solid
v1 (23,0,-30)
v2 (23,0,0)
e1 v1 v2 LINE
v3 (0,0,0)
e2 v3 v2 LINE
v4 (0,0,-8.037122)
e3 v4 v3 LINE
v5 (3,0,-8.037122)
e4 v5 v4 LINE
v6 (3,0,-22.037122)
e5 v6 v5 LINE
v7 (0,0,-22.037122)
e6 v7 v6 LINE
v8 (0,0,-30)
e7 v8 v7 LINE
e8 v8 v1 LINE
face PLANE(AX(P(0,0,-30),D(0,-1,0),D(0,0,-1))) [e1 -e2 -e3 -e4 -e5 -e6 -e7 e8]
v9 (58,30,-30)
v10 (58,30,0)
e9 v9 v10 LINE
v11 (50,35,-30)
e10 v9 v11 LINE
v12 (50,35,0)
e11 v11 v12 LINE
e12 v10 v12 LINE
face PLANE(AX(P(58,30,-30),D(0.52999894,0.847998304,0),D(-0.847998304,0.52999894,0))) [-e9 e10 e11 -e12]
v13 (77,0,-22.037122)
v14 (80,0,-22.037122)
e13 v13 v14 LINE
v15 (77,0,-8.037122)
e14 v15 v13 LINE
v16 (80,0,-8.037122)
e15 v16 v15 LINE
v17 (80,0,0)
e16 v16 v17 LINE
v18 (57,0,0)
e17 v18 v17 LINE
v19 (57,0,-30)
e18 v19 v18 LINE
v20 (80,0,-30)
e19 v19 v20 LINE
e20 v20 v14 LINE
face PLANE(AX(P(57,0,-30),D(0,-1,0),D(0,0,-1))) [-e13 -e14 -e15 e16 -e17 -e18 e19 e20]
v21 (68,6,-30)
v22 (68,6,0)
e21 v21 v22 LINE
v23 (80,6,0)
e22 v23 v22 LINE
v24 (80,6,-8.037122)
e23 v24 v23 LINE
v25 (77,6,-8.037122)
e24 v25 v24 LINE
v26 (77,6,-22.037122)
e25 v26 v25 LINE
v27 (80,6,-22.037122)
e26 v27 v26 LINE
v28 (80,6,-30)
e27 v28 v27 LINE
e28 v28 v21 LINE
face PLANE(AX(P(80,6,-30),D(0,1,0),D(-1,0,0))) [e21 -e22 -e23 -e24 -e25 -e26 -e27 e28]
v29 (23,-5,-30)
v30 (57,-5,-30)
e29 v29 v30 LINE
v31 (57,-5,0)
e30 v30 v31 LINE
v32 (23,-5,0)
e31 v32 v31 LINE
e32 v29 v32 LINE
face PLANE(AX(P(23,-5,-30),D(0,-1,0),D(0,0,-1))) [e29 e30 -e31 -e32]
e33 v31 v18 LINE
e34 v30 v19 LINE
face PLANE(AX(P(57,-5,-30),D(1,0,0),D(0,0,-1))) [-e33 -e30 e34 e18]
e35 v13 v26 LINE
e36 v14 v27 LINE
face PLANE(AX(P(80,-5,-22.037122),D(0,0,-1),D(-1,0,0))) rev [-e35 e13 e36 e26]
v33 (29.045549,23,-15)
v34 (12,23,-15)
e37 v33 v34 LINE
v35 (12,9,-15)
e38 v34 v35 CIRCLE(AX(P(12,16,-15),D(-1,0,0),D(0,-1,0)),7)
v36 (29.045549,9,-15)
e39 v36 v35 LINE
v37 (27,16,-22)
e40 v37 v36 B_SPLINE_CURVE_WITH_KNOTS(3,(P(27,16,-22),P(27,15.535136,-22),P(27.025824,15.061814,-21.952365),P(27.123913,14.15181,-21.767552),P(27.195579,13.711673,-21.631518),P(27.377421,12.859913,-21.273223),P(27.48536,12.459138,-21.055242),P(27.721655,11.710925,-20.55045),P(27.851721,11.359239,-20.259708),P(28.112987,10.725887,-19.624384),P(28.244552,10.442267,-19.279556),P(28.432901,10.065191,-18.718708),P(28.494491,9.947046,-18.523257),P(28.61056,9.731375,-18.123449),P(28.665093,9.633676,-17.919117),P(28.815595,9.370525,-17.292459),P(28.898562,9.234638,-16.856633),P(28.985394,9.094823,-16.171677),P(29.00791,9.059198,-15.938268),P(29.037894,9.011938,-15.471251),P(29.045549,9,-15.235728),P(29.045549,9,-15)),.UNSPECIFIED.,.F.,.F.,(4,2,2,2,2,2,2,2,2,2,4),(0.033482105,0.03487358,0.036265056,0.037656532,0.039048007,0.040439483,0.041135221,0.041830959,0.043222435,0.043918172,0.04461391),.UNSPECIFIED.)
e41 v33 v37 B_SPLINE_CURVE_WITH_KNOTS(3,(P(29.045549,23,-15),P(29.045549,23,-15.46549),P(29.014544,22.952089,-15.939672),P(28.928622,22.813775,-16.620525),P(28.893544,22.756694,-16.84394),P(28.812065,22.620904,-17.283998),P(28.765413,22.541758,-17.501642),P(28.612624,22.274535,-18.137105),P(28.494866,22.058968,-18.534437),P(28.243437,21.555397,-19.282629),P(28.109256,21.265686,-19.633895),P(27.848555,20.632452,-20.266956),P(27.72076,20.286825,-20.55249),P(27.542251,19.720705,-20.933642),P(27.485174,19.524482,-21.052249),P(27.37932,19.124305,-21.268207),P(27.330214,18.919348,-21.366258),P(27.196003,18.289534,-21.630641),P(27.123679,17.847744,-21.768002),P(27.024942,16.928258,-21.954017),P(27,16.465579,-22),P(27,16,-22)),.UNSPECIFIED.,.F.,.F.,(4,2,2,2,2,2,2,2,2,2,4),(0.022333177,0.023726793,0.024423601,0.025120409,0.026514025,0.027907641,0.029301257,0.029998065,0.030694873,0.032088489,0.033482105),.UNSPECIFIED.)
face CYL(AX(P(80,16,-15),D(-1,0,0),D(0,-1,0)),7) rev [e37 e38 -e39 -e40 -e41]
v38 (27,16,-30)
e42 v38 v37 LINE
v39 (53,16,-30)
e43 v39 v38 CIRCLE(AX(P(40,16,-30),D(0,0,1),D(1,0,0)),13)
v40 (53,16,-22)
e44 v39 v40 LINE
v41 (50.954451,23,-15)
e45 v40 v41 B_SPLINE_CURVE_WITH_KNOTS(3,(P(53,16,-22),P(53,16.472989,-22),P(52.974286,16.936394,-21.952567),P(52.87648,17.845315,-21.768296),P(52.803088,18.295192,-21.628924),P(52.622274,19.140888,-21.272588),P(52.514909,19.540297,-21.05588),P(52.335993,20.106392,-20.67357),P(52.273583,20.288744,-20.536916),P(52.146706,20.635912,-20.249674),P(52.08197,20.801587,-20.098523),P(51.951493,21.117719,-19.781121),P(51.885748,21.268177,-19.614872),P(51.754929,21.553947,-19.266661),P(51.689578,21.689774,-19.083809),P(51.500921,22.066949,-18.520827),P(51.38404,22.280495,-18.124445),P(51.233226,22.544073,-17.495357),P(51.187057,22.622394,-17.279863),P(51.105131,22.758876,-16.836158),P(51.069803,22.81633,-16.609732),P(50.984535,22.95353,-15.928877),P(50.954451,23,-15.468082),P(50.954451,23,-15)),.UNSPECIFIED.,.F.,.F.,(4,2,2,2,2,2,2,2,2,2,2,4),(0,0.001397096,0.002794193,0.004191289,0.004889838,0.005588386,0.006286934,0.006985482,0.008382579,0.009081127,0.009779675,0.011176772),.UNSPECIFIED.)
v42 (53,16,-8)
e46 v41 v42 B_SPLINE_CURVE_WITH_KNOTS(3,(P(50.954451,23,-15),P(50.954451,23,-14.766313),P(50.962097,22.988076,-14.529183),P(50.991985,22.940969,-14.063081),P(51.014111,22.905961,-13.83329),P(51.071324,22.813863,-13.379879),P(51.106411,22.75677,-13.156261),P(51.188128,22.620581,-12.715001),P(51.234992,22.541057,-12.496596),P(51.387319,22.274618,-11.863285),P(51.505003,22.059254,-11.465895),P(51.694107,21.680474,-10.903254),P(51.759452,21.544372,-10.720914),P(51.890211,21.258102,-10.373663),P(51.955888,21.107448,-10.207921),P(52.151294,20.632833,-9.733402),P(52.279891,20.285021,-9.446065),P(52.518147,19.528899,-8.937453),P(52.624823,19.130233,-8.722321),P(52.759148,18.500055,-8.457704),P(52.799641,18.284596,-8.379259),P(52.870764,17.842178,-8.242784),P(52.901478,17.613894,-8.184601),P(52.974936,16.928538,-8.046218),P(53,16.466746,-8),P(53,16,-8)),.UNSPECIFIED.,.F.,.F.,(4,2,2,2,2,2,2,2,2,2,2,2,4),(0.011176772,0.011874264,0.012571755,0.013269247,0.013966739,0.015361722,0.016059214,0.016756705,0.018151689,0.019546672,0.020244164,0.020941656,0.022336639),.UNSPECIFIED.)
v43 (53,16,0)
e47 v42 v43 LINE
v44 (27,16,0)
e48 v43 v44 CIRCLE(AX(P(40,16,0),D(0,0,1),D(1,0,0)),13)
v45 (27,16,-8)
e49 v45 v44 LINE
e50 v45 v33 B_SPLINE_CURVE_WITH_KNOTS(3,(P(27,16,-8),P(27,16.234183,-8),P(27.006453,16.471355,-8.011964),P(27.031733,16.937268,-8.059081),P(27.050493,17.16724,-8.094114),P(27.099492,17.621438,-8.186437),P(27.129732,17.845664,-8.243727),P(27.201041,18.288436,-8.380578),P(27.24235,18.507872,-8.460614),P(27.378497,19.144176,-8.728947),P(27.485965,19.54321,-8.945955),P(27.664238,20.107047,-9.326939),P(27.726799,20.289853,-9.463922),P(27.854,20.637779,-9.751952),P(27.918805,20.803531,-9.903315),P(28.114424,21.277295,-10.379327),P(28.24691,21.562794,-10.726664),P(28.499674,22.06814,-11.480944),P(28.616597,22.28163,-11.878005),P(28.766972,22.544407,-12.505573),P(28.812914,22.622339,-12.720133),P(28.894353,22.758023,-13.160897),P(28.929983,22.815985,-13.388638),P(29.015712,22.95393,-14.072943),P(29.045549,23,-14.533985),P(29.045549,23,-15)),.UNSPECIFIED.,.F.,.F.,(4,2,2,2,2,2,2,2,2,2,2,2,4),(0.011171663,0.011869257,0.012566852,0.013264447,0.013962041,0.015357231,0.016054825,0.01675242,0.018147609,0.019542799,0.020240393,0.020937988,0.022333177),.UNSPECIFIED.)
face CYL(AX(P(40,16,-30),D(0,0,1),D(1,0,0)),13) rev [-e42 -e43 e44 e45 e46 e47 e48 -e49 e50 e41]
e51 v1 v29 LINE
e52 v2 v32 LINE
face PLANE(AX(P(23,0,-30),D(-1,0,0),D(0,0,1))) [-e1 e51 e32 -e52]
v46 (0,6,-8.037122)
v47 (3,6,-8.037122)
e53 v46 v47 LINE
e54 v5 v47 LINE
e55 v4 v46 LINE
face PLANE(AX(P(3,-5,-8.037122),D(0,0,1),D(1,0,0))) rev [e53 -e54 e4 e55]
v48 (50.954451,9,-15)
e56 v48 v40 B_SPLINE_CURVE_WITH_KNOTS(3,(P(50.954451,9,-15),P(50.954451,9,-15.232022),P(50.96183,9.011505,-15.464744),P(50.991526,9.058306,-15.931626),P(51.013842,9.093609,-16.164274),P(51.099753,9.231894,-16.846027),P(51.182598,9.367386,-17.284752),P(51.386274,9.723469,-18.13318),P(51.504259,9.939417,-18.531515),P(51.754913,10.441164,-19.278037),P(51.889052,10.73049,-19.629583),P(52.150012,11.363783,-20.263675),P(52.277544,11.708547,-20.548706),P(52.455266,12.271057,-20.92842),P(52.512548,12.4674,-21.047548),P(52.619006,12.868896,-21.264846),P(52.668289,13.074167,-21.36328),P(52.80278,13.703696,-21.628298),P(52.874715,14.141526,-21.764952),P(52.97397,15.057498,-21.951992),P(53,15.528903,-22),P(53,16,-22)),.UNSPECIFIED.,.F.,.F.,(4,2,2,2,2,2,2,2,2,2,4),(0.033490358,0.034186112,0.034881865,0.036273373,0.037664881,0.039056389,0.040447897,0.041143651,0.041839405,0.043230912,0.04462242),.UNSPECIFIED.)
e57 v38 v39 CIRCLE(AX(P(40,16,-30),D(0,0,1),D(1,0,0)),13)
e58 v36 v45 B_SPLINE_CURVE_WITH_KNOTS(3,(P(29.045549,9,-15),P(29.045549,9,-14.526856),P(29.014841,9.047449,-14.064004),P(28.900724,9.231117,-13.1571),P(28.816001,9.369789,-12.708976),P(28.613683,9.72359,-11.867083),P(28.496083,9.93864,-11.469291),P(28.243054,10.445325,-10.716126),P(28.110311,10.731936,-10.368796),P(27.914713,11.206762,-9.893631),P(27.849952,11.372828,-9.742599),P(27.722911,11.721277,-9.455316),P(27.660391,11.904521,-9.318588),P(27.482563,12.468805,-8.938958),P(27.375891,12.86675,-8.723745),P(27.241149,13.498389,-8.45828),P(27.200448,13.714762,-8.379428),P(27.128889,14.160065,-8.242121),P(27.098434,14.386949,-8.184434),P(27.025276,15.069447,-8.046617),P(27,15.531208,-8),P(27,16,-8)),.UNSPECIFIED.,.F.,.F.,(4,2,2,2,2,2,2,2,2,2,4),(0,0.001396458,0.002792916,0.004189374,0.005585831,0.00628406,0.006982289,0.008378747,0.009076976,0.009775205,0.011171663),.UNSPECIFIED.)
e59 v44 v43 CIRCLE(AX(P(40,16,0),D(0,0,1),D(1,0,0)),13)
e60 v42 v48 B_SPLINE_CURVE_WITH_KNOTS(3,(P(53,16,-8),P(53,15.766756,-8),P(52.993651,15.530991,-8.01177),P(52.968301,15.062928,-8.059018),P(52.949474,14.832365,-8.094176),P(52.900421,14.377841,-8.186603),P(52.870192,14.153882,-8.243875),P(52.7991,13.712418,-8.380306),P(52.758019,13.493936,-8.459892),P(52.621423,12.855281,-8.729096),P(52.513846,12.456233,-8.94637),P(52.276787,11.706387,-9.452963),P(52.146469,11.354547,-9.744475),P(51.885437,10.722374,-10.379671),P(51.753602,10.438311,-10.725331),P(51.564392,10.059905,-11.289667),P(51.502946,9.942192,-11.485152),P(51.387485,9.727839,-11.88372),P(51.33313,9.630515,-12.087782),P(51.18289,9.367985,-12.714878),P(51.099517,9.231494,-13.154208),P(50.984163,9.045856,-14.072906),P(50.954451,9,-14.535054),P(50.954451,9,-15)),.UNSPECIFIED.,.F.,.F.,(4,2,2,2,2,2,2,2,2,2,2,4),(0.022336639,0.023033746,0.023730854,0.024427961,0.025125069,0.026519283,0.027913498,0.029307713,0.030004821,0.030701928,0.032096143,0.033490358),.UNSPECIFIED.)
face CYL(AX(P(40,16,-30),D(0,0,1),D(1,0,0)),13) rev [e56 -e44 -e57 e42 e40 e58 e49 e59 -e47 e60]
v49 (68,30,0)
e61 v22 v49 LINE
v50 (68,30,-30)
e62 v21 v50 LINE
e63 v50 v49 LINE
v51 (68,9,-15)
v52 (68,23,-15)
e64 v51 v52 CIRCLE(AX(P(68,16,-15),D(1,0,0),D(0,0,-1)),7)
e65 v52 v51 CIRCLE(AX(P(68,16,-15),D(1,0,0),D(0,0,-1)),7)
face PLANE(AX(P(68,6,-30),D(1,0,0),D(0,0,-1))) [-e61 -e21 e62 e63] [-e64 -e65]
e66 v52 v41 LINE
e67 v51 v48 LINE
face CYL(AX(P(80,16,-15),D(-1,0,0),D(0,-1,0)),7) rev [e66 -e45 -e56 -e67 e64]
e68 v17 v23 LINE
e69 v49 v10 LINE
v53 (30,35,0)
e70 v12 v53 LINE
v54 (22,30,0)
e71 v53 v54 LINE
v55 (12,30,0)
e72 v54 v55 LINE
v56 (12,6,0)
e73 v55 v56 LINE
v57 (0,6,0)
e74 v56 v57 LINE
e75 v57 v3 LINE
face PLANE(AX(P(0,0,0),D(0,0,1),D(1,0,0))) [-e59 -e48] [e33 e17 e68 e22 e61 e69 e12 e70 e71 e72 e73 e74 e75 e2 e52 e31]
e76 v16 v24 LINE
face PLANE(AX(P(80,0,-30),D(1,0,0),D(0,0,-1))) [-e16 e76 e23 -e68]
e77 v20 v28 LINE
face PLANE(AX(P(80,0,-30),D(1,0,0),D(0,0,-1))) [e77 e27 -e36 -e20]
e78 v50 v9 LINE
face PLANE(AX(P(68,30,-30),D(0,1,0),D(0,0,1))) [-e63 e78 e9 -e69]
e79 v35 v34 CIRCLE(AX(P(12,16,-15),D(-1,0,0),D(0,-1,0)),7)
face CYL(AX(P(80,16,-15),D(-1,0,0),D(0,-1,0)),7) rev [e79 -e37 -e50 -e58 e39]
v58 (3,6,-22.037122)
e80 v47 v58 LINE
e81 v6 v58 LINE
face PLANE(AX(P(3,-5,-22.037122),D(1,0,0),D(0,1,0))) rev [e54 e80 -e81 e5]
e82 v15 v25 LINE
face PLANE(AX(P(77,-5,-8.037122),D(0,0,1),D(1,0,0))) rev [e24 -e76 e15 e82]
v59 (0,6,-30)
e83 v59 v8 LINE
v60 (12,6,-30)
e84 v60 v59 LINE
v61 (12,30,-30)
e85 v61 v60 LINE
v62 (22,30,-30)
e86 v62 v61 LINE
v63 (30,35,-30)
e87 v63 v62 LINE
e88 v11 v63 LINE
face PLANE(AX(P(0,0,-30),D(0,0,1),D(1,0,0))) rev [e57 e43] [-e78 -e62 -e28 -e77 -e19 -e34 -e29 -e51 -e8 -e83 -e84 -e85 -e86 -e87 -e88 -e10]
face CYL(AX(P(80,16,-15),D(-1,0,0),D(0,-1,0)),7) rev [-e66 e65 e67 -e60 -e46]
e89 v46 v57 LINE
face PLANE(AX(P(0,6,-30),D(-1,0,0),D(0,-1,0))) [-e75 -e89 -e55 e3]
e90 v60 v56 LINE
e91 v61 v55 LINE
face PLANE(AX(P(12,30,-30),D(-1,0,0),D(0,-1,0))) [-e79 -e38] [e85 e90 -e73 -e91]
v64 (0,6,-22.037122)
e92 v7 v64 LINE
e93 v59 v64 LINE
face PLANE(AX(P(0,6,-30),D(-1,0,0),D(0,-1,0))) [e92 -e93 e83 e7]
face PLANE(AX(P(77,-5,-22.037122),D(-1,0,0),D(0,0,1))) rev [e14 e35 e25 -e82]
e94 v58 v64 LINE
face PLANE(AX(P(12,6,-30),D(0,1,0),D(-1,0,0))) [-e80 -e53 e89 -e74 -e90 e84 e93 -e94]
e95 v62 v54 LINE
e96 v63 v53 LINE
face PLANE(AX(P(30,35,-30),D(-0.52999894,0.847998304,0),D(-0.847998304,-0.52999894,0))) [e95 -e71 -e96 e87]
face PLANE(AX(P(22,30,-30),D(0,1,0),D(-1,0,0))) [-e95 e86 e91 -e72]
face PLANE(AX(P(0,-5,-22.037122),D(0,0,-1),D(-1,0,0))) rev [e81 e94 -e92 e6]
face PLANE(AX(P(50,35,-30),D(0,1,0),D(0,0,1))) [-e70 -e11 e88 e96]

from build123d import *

# Parameters (mm, degrees)
BLOCK_PROFILE_SKETCH_R   = 13
BLOCK_BODY_DEPTH         = 30
TOP_GROOVE_SKETCH_W      = 3
TOP_GROOVE_SKETCH_H      = 14
TOP_GROOVE_CUT_DEPTH     = 91.227490268
SIDE_CROSS_HOLE_SKETCH_R = 7
SIDE_CROSS_HOLE_DEPTH    = 83.152297594


with BuildPart() as part:
    # Block Profile Sketch → Block Body (new body)
    with BuildSketch(Plane.XY):
        Polygon((0, 0), (23, 0), (23, -5), (57, -5), (57, 0), (80, 0), (80, 6), (68, 6), (68, 30), (58, 30), (50, 35), (30, 35), (22, 30), (12, 30), (12, 6), (0, 6), align=None)
        with Locations((40, 16)):
            Circle(BLOCK_PROFILE_SKETCH_R, mode=Mode.SUBTRACT)
    extrude(amount=-BLOCK_BODY_DEPTH)

    # Top Groove Sketch → Top Groove Cut (cut, through all)
    with BuildSketch(Plane(origin=(0, 6, 0), x_dir=(1, 0, 0), z_dir=(0, 1, 0))):
        with Locations((1.5, 15.037121503)):
            Rectangle(TOP_GROOVE_SKETCH_W, TOP_GROOVE_SKETCH_H)
        with Locations((78.5, 15.037121503)):
            Rectangle(TOP_GROOVE_SKETCH_W, TOP_GROOVE_SKETCH_H)
    extrude(amount=-TOP_GROOVE_CUT_DEPTH, mode=Mode.SUBTRACT)

    # Side Cross Hole Sketch → Side Cross Hole (cut, through all)
    with BuildSketch(Plane.ZY.offset(-12)):
        with Locations(Location((-15, 16, 0), (0, 0, 270))):
            Circle(SIDE_CROSS_HOLE_SKETCH_R)
    extrude(amount=-SIDE_CROSS_HOLE_DEPTH, mode=Mode.SUBTRACT)


solid = part.part
